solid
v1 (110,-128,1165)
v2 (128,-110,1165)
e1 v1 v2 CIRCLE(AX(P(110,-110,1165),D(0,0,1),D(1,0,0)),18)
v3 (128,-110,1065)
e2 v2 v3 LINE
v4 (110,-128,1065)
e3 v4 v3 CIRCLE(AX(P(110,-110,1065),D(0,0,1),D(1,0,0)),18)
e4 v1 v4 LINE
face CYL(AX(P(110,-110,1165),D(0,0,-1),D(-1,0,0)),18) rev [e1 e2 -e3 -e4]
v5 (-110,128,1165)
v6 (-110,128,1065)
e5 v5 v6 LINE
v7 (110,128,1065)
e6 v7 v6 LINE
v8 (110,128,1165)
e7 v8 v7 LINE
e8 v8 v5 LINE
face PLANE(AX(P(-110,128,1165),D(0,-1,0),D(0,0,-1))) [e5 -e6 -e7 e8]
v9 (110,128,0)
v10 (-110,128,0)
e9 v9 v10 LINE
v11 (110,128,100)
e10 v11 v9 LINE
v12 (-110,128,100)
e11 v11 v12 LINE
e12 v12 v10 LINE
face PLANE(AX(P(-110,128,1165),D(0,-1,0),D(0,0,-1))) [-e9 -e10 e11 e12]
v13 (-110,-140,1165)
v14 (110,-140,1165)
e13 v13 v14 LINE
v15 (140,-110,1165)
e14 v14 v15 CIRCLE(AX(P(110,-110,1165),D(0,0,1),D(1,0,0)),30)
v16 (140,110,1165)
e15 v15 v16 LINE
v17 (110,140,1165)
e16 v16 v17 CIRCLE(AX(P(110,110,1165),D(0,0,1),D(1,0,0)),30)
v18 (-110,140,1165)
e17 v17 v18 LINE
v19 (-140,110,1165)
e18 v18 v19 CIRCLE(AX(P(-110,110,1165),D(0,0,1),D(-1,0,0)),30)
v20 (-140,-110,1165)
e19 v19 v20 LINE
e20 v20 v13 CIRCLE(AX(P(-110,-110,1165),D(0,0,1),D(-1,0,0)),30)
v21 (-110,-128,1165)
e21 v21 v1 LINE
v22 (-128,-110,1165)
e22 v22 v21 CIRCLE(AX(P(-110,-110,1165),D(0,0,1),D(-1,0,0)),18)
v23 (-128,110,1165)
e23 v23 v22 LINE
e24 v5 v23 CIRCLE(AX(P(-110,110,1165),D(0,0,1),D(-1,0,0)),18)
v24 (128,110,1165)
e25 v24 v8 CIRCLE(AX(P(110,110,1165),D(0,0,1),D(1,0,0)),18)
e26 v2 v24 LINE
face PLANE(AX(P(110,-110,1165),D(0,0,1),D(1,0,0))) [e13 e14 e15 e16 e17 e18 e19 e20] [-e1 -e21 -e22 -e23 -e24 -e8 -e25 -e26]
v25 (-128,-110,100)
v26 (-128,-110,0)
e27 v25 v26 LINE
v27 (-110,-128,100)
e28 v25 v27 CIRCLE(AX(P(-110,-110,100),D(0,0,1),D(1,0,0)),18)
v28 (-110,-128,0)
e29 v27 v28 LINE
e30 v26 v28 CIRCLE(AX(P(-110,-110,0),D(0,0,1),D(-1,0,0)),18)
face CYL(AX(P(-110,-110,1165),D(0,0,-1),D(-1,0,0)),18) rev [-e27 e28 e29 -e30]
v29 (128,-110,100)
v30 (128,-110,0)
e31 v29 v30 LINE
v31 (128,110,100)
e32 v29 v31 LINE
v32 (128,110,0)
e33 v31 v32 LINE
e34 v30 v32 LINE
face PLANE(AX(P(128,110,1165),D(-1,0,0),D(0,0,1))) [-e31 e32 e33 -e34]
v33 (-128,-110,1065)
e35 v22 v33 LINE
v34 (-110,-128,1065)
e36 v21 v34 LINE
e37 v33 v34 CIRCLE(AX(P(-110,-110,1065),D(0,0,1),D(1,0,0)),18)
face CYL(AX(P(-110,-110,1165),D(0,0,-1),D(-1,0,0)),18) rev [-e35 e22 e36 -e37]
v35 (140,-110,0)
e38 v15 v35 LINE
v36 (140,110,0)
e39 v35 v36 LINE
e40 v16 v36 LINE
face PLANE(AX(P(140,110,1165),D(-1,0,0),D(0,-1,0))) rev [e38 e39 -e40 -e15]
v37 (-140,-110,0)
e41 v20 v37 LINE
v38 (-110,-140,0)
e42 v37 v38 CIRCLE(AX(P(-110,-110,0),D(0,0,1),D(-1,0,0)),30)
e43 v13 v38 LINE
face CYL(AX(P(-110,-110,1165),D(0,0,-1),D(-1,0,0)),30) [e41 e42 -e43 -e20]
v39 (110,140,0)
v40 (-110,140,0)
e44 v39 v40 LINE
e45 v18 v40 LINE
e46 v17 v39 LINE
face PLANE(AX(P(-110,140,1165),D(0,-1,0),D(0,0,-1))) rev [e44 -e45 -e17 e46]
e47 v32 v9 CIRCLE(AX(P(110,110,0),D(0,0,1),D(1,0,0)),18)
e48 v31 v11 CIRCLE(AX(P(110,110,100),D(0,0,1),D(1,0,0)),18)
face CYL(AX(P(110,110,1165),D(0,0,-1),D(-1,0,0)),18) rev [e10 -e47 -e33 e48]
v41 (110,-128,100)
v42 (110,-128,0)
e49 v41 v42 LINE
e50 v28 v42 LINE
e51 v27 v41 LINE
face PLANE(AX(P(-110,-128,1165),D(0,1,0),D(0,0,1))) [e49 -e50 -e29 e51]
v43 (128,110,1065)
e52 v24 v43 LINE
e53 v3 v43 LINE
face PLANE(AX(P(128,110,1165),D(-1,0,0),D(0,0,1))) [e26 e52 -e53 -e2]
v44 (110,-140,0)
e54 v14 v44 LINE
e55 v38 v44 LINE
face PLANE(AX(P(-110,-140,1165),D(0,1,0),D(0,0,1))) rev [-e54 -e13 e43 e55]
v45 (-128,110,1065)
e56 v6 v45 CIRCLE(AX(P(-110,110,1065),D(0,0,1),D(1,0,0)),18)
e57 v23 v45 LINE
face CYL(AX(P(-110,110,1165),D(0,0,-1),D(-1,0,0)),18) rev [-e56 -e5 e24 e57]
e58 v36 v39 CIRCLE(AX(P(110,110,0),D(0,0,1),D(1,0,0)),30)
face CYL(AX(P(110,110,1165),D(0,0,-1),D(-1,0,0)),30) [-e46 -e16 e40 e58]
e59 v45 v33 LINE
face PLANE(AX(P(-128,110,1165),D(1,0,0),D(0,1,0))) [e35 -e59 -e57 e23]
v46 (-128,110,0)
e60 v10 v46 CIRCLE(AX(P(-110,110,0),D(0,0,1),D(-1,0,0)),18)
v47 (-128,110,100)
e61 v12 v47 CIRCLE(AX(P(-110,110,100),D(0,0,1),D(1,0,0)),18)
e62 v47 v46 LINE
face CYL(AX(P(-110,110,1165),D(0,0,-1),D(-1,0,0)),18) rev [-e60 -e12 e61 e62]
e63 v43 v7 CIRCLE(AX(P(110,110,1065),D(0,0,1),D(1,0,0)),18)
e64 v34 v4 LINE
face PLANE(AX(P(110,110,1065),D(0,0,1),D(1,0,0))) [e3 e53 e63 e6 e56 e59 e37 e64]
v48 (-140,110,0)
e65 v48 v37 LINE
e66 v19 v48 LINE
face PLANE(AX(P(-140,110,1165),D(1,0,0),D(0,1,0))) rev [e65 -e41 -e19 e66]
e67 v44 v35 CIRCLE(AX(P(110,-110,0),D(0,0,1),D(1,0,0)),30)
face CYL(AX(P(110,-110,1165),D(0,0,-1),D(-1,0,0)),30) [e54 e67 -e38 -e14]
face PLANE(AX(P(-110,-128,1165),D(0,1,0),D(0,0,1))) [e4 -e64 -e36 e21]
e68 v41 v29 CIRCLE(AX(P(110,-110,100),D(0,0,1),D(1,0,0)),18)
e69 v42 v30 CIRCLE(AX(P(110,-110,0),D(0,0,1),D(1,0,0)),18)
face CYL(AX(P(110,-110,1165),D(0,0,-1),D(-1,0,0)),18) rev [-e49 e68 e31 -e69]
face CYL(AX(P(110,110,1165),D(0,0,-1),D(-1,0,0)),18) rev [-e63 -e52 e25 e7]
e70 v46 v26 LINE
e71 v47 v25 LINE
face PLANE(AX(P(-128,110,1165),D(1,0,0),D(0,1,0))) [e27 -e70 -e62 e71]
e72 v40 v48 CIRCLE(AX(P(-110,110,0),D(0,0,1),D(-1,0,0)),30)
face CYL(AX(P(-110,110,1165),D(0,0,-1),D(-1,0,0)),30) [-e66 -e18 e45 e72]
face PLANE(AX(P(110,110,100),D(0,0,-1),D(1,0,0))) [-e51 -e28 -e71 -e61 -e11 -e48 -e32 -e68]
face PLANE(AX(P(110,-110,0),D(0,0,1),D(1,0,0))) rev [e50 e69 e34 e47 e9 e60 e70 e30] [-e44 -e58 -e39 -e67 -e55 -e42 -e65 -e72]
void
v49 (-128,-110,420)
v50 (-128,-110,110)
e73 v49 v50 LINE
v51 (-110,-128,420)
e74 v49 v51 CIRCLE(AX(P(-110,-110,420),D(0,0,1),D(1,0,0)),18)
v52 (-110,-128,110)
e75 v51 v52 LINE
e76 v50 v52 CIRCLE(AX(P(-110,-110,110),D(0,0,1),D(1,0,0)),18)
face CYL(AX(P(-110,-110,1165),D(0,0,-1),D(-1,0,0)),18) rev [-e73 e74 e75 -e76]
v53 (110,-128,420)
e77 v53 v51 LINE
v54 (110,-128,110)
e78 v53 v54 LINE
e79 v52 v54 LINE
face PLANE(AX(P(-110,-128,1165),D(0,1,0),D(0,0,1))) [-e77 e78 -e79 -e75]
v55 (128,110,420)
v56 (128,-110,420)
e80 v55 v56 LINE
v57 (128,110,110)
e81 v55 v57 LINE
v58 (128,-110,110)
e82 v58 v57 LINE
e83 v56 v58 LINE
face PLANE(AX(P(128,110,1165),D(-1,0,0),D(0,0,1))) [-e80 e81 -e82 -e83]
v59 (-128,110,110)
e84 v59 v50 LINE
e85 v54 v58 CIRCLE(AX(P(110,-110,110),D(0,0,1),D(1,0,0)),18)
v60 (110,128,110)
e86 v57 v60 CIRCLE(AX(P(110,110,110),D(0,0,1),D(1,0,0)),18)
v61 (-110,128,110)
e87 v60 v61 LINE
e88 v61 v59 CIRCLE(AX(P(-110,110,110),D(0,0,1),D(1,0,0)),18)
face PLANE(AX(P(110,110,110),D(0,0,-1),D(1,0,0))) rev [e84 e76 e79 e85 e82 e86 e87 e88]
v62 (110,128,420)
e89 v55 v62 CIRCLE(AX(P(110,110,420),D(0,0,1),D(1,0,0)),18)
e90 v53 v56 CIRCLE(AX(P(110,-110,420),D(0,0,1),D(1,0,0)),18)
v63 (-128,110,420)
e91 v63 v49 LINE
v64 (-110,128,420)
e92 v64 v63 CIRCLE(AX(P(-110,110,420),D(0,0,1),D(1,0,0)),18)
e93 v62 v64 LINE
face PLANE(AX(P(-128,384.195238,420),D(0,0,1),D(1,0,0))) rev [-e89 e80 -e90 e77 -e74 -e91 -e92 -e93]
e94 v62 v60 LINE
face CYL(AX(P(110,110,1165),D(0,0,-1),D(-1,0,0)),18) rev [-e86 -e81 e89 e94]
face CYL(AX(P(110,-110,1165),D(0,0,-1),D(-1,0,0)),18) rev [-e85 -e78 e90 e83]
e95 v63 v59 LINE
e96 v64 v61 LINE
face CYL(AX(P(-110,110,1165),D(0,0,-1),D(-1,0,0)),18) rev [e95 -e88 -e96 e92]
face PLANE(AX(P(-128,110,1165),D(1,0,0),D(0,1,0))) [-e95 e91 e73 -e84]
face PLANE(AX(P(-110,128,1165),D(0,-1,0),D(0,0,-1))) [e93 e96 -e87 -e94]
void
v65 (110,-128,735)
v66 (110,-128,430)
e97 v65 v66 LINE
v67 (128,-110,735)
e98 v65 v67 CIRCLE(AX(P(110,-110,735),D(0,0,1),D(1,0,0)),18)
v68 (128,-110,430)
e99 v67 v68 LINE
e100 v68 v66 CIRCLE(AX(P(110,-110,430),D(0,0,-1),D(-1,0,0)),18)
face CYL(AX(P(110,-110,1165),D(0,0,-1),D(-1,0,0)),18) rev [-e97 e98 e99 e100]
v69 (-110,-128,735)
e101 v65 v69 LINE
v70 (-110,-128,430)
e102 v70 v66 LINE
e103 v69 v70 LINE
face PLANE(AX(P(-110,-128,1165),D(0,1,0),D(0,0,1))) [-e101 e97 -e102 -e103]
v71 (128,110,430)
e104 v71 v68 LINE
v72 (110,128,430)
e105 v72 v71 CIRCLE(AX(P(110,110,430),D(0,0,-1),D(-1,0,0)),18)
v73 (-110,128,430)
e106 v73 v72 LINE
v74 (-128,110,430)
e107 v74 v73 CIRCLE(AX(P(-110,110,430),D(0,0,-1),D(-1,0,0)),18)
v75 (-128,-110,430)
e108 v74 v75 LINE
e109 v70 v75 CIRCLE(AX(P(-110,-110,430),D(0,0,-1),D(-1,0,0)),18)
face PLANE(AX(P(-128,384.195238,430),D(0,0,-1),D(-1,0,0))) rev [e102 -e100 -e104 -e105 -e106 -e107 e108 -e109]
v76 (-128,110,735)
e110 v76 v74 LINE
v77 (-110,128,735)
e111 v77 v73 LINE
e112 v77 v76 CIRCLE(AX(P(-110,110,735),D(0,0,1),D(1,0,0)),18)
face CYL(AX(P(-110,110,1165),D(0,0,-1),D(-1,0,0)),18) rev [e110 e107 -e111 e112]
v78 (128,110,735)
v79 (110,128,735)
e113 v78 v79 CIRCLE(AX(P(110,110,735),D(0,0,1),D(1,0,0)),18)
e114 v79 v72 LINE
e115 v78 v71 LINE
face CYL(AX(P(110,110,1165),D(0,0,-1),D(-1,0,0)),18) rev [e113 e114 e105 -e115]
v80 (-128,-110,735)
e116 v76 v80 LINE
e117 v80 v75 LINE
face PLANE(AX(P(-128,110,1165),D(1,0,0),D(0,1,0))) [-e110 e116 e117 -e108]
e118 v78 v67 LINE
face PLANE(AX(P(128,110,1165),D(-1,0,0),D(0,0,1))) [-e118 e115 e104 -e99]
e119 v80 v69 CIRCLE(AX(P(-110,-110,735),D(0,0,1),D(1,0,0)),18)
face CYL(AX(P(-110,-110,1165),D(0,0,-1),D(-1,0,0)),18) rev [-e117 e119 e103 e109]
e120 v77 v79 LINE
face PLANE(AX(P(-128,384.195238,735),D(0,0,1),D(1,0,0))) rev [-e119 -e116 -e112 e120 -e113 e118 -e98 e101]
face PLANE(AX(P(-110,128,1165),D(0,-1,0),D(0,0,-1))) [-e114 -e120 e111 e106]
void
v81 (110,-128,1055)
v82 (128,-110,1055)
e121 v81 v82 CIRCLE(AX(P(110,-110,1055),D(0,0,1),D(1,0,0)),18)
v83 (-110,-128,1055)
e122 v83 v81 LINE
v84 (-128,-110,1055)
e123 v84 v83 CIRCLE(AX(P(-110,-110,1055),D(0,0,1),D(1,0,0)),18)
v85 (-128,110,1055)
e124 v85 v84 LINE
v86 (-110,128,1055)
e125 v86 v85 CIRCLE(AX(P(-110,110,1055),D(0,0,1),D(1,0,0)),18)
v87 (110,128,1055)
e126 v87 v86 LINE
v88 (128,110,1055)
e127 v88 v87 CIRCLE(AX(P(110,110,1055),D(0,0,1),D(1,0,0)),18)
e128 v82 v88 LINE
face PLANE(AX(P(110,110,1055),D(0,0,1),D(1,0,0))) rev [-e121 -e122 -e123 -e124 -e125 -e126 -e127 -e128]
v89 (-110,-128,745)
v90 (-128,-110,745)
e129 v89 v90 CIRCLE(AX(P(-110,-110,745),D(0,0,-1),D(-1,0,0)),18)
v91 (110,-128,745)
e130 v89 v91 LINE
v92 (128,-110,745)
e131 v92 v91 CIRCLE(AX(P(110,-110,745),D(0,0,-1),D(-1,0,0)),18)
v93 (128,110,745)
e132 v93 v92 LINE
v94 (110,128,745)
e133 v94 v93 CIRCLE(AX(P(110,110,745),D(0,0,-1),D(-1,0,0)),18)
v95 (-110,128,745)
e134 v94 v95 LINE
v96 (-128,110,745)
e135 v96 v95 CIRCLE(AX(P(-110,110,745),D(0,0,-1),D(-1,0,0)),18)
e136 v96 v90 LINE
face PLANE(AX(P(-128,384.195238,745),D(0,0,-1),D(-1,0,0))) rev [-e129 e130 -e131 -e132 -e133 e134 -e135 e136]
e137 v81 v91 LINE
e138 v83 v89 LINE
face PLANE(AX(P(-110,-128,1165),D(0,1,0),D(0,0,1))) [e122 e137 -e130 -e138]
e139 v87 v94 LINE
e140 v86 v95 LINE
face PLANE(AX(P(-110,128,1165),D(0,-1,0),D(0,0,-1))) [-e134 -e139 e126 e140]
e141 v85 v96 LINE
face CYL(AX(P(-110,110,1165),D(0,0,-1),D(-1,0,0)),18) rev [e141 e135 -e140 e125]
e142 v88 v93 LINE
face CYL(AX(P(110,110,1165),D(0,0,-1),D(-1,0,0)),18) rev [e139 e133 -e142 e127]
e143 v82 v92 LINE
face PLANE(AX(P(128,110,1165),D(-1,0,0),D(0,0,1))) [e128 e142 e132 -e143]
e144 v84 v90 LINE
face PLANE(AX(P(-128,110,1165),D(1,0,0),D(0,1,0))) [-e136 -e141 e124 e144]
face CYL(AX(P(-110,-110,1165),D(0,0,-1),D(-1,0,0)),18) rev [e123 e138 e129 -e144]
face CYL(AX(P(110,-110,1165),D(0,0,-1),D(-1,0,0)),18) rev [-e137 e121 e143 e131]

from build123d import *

# Parameters (mm, degrees)
EXTRUDE_1_DEPTH = 1165
EXTRUDE_START   = -110
EXTRUDE_2_DEPTH = 10
EXTRUDE_4_REACH = 1205.598
SKETCH_4_W      = 256
SKETCH_4_H      = 10


with BuildPart() as part:
    # 草图1 → 凸台-拉伸1 (new body)
    with BuildSketch(Plane.XY):
        with BuildLine():
            Line((-110, 140), (110, 140))
            ThreePointArc((110, 140), (131.213203436, 131.213203436), (140, 110))
            Line((140, 110), (140, -110))
            ThreePointArc((140, -110), (131.213203436, -131.213203436), (110, -140))
            Line((110, -140), (-110, -140))
            ThreePointArc((-110, -140), (-131.213203436, -131.213203436), (-140, -110))
            Line((-140, -110), (-140, 110))
            ThreePointArc((-140, 110), (-131.213203436, 131.213203436), (-110, 140))
        make_face()
        with BuildLine():
            Line((-110, 128), (110, 128))
            ThreePointArc((110, 128), (122.727922061, 122.727922061), (128, 110))
            Line((128, 110), (128, -110))
            ThreePointArc((128, -110), (122.727922061, -122.727922061), (110, -128))
            Line((110, -128), (-110, -128))
            ThreePointArc((-110, -128), (-122.727922061, -122.727922061), (-128, -110))
            Line((-128, -110), (-128, 110))
            ThreePointArc((-128, 110), (-122.727922061, 122.727922061), (-110, 128))
        make_face(mode=Mode.SUBTRACT)
    extrude(amount=EXTRUDE_1_DEPTH)

    # 草图2 → 凸台-拉伸2 (add)
    with BuildSketch(Plane.XY.offset(1165).offset(EXTRUDE_START)):
        with BuildLine():
            Line((128, -110), (128, 110))
            ThreePointArc((128, 110), (122.727922061, 122.727922061), (110, 128))
            Line((110, 128), (-110, 128))
            ThreePointArc((-110, 128), (-122.727922061, 122.727922061), (-128, 110))
            Line((-128, 110), (-128, -110))
            ThreePointArc((-128, -110), (-122.727922061, -122.727922061), (-110, -128))
            Line((-110, -128), (110, -128))
            ThreePointArc((110, -128), (122.727922061, -122.727922061), (128, -110))
        make_face()
    extrude_2 = extrude(amount=EXTRUDE_2_DEPTH)

    # 镜向1: 凸台-拉伸2 across plane
    add(extrude_2.mirror(Plane.XY.offset(582.5)))

    # 凸台-拉伸4: up to this face of the body (flat: up to its plane)
    extrude_4_end = Plane(part.part.faces().sort_by_distance((0, 128, 50))[0])
    # 草图4 → 凸台-拉伸4 (add, up to the picked face)
    with BuildSketch(Plane(origin=(0, -128, 0), x_dir=(1, 0, 0), z_dir=(0, 1, 0)), mode=Mode.PRIVATE) as extrude_4_sk1:
        with Locations((0, -740)):
            Rectangle(SKETCH_4_W, SKETCH_4_H)
    extrude_4_tool1 = split(extrude(extrude_4_sk1.sketch, amount=EXTRUDE_4_REACH, mode=Mode.PRIVATE), bisect_by=extrude_4_end, keep=Keep.BOTH, mode=Mode.PRIVATE)
    # 草图4 → 凸台-拉伸4 (add, up to the picked face)
    with BuildSketch(Plane(origin=(0, -128, 0), x_dir=(1, 0, 0), z_dir=(0, 1, 0)), mode=Mode.PRIVATE) as extrude_4_sk2:
        with Locations((0, -425)):
            Rectangle(SKETCH_4_W, SKETCH_4_H)
    extrude_4_tool2 = split(extrude(extrude_4_sk2.sketch, amount=EXTRUDE_4_REACH, mode=Mode.PRIVATE), bisect_by=extrude_4_end, keep=Keep.BOTH, mode=Mode.PRIVATE)
    add(extrude_4_tool1.solids().sort_by(Axis((0, -128, 740), (0, 1, 0)))[0])
    add(extrude_4_tool2.solids().sort_by(Axis((0, -128, 425), (0, 1, 0)))[0])


solid = part.part
